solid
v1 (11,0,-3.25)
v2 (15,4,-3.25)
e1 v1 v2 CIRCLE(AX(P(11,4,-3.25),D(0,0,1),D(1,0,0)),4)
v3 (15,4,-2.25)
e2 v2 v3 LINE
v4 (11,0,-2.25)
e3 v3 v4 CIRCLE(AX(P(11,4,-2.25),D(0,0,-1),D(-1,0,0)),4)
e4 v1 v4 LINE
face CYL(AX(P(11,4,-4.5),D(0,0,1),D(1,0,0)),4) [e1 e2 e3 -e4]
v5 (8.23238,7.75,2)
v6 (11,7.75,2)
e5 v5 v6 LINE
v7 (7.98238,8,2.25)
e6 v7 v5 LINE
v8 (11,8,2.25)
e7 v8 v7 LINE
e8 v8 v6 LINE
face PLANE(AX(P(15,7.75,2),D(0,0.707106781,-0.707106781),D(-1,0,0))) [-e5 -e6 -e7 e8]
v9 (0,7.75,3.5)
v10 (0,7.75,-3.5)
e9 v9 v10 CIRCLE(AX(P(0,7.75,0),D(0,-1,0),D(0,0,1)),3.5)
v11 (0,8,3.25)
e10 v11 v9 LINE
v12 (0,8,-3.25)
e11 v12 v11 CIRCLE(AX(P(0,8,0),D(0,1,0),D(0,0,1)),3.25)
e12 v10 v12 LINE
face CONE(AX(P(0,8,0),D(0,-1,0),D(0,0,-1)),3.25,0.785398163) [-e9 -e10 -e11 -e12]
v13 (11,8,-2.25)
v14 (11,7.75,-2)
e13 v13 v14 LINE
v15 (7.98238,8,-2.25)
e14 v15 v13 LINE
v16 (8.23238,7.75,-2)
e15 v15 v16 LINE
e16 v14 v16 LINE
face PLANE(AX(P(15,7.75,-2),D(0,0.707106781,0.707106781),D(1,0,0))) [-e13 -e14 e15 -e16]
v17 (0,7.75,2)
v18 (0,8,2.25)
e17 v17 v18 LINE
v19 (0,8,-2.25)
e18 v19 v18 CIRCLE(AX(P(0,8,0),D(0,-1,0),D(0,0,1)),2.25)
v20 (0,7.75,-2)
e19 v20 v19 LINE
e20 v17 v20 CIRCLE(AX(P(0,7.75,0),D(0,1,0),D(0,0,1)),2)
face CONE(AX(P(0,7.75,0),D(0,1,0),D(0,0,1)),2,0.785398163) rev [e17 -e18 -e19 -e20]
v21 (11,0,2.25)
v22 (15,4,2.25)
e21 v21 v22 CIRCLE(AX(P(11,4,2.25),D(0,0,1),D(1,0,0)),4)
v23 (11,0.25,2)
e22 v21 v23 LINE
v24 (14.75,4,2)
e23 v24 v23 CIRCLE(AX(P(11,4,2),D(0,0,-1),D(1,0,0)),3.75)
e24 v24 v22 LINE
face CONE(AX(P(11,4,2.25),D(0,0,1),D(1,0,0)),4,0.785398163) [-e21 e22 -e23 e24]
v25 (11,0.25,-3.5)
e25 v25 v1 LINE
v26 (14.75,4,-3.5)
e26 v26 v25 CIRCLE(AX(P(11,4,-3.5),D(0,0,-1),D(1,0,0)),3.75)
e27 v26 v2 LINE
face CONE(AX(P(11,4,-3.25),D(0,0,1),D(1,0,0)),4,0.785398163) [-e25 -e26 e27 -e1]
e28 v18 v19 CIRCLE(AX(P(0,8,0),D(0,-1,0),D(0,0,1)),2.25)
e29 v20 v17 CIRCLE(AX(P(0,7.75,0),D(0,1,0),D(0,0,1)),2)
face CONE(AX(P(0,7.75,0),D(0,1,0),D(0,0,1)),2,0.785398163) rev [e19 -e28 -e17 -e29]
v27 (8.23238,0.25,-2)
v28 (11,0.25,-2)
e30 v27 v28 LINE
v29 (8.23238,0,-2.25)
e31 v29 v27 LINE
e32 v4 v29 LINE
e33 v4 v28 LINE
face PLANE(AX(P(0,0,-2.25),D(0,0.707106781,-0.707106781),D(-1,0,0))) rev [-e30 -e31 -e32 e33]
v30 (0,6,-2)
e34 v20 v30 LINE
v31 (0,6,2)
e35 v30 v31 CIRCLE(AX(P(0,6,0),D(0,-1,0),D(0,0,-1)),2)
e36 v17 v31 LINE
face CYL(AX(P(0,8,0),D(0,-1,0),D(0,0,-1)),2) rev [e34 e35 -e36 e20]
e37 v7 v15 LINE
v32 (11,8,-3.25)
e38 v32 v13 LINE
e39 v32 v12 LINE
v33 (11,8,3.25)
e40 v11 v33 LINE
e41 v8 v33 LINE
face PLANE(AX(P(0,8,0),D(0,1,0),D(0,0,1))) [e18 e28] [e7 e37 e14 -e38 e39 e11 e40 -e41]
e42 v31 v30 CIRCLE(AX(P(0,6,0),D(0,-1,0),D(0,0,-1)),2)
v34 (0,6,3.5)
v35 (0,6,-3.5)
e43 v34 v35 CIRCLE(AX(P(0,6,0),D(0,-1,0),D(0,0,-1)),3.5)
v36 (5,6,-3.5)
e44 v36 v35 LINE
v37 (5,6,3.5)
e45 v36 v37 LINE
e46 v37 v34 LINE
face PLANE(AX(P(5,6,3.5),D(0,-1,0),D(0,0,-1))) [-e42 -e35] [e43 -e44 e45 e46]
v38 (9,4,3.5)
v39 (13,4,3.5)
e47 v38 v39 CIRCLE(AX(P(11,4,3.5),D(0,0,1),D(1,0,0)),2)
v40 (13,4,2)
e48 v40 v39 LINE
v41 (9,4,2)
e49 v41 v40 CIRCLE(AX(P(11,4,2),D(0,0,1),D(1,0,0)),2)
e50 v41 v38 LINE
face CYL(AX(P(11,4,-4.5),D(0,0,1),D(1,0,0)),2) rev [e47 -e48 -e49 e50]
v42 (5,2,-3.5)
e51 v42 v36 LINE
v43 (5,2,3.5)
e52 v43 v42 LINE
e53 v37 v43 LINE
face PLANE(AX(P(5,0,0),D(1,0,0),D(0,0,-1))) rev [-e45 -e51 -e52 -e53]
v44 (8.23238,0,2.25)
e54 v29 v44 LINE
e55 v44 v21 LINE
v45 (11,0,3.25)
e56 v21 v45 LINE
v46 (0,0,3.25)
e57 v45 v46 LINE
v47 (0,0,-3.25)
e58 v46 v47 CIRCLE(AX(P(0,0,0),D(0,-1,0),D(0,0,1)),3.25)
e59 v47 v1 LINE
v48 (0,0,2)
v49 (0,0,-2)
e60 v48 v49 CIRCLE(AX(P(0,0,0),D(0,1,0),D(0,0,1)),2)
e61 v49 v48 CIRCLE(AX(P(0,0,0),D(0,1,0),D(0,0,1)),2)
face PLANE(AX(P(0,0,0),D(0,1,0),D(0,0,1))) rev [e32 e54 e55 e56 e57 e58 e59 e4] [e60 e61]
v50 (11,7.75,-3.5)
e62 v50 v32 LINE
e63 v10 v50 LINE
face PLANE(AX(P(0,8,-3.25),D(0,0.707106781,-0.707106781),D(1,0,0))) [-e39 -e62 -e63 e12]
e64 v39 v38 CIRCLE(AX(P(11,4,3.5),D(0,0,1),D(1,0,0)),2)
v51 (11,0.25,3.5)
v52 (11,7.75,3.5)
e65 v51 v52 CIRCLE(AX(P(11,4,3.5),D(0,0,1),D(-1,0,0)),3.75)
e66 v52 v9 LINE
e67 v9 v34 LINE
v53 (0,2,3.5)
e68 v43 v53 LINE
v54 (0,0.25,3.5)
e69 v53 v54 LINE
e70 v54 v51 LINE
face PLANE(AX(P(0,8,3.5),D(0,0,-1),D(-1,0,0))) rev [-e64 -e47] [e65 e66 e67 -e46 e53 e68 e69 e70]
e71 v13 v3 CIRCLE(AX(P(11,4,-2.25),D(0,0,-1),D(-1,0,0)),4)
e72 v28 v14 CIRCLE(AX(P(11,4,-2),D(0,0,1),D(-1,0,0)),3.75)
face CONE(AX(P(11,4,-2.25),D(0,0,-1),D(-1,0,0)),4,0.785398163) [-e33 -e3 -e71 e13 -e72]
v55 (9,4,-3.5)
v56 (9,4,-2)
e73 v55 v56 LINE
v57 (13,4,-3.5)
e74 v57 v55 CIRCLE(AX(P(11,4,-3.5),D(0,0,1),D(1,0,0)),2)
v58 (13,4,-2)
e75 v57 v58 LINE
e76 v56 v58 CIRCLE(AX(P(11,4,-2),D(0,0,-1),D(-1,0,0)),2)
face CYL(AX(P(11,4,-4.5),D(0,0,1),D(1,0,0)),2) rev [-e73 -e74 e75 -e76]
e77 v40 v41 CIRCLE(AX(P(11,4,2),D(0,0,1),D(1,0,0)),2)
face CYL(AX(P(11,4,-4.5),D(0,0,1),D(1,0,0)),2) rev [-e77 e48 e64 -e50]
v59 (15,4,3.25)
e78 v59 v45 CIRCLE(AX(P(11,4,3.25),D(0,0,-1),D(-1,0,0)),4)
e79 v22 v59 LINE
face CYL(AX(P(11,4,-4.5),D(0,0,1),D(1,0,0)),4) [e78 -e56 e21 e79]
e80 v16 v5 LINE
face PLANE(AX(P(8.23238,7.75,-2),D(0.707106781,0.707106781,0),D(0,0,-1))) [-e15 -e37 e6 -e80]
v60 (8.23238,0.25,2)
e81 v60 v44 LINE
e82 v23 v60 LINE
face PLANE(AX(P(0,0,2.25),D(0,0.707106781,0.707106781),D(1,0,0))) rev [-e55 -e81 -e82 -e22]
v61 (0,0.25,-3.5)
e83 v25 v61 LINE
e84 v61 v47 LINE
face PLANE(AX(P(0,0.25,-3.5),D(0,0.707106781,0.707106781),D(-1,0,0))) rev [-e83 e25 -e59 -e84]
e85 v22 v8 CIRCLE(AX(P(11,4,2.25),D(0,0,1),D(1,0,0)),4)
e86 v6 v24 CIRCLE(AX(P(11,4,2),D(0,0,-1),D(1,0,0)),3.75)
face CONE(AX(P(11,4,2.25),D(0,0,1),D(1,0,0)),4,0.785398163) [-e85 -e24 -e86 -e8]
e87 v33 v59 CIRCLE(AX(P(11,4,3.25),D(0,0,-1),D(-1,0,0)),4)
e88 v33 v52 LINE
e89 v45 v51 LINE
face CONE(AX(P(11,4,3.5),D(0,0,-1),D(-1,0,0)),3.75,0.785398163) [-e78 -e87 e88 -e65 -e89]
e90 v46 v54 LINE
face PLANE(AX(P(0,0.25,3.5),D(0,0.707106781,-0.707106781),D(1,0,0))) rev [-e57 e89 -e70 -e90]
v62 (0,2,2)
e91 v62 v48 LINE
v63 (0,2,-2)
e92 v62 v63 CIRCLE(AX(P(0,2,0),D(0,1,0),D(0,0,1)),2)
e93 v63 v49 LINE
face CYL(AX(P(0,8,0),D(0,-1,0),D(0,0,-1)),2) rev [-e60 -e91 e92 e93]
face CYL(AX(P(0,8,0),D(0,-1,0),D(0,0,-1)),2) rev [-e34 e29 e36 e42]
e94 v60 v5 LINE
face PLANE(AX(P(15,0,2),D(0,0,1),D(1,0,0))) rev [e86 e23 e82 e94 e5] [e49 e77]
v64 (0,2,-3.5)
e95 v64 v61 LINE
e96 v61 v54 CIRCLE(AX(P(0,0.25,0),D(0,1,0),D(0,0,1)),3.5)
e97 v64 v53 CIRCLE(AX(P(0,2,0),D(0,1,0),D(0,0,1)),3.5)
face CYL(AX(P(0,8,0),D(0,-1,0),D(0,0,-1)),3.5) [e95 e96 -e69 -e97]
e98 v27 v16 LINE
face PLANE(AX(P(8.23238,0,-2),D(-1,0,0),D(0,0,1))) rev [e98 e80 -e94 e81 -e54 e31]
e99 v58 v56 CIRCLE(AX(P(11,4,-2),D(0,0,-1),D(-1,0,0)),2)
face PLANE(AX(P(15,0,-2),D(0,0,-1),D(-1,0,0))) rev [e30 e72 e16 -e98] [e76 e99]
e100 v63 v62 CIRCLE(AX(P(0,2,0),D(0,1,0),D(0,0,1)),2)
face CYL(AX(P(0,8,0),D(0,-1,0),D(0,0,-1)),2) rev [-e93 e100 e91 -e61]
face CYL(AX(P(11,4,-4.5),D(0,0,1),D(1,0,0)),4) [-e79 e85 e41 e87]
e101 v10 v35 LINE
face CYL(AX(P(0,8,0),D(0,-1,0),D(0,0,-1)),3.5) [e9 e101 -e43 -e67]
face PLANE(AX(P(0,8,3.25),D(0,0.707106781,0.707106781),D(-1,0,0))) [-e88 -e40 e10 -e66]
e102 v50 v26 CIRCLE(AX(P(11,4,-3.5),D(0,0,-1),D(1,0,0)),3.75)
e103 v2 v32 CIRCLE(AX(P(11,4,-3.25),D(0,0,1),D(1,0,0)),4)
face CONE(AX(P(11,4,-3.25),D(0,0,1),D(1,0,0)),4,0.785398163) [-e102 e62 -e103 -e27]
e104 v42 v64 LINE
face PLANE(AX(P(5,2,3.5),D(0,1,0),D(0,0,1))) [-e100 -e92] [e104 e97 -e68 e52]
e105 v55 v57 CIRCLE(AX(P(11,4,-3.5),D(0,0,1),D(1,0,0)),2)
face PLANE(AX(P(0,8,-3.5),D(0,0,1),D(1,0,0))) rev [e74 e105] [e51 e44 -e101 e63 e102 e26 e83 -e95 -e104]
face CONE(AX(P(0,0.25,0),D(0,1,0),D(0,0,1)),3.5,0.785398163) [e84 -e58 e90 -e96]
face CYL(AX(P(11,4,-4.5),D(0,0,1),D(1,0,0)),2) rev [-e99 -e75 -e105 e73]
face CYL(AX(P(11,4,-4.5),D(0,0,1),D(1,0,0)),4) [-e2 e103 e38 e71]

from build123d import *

# Parameters (mm, degrees)
SKETCH1_R               = 4
BOSS_EXTRUDE1_DEPTH     = 16
SKETCH2_W               = 13.535239133
SKETCH2_H               = 8
CUT_EXTRUDE1_DEPTH      = 16
SKETCH3_R               = 4
CUT_EXTRUDE2_DEPTH      = 16
CUT_EXTRUDE3_DEPTH      = 10
CUT_EXTRUDE3_DEPTH_BACK = 16
SKETCH4_W               = 14
SKETCH4_H               = 8
CHAMFER1_SIZE           = 0.5
SCALE1_SCALE            = 0.5


with BuildPart() as part:
    # Sketch1 → Boss-Extrude1 (new body)
    with BuildSketch(Plane(origin=(0, 0, 0), x_dir=(1, 0, 0), z_dir=(0, 1, 0))):
        with BuildLine():
            Line((0, 7), (30, 7))
            Line((30, 7), (30, -7))
            Line((30, -7), (0, -7))
            ThreePointArc((0, -7), (-7, 0), (0, 7))
        make_face()
        with Locations(Location((0, 0, 0), (0, 0, 270))):
            Circle(SKETCH1_R, mode=Mode.SUBTRACT)
    extrude(amount=BOSS_EXTRUDE1_DEPTH)

    # Sketch2 → Cut-Extrude1 (cut)
    with BuildSketch(Plane(origin=(0, 16, 0), x_dir=(1, 0, 0), z_dir=(0, 1, 0))):
        with Locations((23.232380434, 0)):
            Rectangle(SKETCH2_W, SKETCH2_H)
    extrude(amount=-CUT_EXTRUDE1_DEPTH, mode=Mode.SUBTRACT)

    # Sketch3 → Cut-Extrude2 (cut)
    with BuildSketch(Plane.XY.offset(7)):
        with BuildLine():
            Line((30, 16), (22, 16))
            ThreePointArc((22, 16), (27.656854238, 13.656854261), (30, 8.000000031))
            Line((30, 8.000000031), (30, 16))
        make_face()
        with BuildLine():
            Line((30, 0), (30, 8.000000031))
            ThreePointArc((30, 8.000000031), (27.656854261, 2.343145762), (22, 0))
            Line((22, 0), (30, 0))
        make_face()
        with Locations((22, 8)):
            Circle(SKETCH3_R)
    extrude(amount=-CUT_EXTRUDE2_DEPTH, mode=Mode.SUBTRACT)

    # Sketch4 → Cut-Extrude3 (cut, two sides: drawn at the far end of the back side and taken through both)
    with BuildSketch(Plane(origin=(0, 0, 0), x_dir=(0, 0, -1), z_dir=(1, 0, 0)).offset(-CUT_EXTRUDE3_DEPTH_BACK)):
        with Locations((0, 8)):
            Rectangle(SKETCH4_W, SKETCH4_H)
    extrude(amount=CUT_EXTRUDE3_DEPTH + CUT_EXTRUDE3_DEPTH_BACK, mode=Mode.SUBTRACT)

    # Chamfer1
    chamfer1_edges = [part.edges().sort_by_distance(p)[0] for p in [
        (0, 16, -4),
        (19.232380434, 0, 4),
        (16.464760867, 16, 0),
        (19.232380434, 16, 4),
        (19.232380434, 16, -4),
        (30, 8, -4),
        (11, 16, -7),
        (30, 8, 7),
        (-7, 16, 0),
        (30, 8, -7),
        (30, 8, 4),
        (11, 0, 7),
        (-7, 0, 0),
        (11, 0, -7),
        (19.232380434, 0, -4),
        (11, 16, 7),
    ]]
    chamfer(chamfer1_edges, length=CHAMFER1_SIZE)


with BuildPart() as part_1:
    # Scale1: scaled about (0, 0, 0)
    add(part.part.scale(SCALE1_SCALE))


solid = part_1.part
